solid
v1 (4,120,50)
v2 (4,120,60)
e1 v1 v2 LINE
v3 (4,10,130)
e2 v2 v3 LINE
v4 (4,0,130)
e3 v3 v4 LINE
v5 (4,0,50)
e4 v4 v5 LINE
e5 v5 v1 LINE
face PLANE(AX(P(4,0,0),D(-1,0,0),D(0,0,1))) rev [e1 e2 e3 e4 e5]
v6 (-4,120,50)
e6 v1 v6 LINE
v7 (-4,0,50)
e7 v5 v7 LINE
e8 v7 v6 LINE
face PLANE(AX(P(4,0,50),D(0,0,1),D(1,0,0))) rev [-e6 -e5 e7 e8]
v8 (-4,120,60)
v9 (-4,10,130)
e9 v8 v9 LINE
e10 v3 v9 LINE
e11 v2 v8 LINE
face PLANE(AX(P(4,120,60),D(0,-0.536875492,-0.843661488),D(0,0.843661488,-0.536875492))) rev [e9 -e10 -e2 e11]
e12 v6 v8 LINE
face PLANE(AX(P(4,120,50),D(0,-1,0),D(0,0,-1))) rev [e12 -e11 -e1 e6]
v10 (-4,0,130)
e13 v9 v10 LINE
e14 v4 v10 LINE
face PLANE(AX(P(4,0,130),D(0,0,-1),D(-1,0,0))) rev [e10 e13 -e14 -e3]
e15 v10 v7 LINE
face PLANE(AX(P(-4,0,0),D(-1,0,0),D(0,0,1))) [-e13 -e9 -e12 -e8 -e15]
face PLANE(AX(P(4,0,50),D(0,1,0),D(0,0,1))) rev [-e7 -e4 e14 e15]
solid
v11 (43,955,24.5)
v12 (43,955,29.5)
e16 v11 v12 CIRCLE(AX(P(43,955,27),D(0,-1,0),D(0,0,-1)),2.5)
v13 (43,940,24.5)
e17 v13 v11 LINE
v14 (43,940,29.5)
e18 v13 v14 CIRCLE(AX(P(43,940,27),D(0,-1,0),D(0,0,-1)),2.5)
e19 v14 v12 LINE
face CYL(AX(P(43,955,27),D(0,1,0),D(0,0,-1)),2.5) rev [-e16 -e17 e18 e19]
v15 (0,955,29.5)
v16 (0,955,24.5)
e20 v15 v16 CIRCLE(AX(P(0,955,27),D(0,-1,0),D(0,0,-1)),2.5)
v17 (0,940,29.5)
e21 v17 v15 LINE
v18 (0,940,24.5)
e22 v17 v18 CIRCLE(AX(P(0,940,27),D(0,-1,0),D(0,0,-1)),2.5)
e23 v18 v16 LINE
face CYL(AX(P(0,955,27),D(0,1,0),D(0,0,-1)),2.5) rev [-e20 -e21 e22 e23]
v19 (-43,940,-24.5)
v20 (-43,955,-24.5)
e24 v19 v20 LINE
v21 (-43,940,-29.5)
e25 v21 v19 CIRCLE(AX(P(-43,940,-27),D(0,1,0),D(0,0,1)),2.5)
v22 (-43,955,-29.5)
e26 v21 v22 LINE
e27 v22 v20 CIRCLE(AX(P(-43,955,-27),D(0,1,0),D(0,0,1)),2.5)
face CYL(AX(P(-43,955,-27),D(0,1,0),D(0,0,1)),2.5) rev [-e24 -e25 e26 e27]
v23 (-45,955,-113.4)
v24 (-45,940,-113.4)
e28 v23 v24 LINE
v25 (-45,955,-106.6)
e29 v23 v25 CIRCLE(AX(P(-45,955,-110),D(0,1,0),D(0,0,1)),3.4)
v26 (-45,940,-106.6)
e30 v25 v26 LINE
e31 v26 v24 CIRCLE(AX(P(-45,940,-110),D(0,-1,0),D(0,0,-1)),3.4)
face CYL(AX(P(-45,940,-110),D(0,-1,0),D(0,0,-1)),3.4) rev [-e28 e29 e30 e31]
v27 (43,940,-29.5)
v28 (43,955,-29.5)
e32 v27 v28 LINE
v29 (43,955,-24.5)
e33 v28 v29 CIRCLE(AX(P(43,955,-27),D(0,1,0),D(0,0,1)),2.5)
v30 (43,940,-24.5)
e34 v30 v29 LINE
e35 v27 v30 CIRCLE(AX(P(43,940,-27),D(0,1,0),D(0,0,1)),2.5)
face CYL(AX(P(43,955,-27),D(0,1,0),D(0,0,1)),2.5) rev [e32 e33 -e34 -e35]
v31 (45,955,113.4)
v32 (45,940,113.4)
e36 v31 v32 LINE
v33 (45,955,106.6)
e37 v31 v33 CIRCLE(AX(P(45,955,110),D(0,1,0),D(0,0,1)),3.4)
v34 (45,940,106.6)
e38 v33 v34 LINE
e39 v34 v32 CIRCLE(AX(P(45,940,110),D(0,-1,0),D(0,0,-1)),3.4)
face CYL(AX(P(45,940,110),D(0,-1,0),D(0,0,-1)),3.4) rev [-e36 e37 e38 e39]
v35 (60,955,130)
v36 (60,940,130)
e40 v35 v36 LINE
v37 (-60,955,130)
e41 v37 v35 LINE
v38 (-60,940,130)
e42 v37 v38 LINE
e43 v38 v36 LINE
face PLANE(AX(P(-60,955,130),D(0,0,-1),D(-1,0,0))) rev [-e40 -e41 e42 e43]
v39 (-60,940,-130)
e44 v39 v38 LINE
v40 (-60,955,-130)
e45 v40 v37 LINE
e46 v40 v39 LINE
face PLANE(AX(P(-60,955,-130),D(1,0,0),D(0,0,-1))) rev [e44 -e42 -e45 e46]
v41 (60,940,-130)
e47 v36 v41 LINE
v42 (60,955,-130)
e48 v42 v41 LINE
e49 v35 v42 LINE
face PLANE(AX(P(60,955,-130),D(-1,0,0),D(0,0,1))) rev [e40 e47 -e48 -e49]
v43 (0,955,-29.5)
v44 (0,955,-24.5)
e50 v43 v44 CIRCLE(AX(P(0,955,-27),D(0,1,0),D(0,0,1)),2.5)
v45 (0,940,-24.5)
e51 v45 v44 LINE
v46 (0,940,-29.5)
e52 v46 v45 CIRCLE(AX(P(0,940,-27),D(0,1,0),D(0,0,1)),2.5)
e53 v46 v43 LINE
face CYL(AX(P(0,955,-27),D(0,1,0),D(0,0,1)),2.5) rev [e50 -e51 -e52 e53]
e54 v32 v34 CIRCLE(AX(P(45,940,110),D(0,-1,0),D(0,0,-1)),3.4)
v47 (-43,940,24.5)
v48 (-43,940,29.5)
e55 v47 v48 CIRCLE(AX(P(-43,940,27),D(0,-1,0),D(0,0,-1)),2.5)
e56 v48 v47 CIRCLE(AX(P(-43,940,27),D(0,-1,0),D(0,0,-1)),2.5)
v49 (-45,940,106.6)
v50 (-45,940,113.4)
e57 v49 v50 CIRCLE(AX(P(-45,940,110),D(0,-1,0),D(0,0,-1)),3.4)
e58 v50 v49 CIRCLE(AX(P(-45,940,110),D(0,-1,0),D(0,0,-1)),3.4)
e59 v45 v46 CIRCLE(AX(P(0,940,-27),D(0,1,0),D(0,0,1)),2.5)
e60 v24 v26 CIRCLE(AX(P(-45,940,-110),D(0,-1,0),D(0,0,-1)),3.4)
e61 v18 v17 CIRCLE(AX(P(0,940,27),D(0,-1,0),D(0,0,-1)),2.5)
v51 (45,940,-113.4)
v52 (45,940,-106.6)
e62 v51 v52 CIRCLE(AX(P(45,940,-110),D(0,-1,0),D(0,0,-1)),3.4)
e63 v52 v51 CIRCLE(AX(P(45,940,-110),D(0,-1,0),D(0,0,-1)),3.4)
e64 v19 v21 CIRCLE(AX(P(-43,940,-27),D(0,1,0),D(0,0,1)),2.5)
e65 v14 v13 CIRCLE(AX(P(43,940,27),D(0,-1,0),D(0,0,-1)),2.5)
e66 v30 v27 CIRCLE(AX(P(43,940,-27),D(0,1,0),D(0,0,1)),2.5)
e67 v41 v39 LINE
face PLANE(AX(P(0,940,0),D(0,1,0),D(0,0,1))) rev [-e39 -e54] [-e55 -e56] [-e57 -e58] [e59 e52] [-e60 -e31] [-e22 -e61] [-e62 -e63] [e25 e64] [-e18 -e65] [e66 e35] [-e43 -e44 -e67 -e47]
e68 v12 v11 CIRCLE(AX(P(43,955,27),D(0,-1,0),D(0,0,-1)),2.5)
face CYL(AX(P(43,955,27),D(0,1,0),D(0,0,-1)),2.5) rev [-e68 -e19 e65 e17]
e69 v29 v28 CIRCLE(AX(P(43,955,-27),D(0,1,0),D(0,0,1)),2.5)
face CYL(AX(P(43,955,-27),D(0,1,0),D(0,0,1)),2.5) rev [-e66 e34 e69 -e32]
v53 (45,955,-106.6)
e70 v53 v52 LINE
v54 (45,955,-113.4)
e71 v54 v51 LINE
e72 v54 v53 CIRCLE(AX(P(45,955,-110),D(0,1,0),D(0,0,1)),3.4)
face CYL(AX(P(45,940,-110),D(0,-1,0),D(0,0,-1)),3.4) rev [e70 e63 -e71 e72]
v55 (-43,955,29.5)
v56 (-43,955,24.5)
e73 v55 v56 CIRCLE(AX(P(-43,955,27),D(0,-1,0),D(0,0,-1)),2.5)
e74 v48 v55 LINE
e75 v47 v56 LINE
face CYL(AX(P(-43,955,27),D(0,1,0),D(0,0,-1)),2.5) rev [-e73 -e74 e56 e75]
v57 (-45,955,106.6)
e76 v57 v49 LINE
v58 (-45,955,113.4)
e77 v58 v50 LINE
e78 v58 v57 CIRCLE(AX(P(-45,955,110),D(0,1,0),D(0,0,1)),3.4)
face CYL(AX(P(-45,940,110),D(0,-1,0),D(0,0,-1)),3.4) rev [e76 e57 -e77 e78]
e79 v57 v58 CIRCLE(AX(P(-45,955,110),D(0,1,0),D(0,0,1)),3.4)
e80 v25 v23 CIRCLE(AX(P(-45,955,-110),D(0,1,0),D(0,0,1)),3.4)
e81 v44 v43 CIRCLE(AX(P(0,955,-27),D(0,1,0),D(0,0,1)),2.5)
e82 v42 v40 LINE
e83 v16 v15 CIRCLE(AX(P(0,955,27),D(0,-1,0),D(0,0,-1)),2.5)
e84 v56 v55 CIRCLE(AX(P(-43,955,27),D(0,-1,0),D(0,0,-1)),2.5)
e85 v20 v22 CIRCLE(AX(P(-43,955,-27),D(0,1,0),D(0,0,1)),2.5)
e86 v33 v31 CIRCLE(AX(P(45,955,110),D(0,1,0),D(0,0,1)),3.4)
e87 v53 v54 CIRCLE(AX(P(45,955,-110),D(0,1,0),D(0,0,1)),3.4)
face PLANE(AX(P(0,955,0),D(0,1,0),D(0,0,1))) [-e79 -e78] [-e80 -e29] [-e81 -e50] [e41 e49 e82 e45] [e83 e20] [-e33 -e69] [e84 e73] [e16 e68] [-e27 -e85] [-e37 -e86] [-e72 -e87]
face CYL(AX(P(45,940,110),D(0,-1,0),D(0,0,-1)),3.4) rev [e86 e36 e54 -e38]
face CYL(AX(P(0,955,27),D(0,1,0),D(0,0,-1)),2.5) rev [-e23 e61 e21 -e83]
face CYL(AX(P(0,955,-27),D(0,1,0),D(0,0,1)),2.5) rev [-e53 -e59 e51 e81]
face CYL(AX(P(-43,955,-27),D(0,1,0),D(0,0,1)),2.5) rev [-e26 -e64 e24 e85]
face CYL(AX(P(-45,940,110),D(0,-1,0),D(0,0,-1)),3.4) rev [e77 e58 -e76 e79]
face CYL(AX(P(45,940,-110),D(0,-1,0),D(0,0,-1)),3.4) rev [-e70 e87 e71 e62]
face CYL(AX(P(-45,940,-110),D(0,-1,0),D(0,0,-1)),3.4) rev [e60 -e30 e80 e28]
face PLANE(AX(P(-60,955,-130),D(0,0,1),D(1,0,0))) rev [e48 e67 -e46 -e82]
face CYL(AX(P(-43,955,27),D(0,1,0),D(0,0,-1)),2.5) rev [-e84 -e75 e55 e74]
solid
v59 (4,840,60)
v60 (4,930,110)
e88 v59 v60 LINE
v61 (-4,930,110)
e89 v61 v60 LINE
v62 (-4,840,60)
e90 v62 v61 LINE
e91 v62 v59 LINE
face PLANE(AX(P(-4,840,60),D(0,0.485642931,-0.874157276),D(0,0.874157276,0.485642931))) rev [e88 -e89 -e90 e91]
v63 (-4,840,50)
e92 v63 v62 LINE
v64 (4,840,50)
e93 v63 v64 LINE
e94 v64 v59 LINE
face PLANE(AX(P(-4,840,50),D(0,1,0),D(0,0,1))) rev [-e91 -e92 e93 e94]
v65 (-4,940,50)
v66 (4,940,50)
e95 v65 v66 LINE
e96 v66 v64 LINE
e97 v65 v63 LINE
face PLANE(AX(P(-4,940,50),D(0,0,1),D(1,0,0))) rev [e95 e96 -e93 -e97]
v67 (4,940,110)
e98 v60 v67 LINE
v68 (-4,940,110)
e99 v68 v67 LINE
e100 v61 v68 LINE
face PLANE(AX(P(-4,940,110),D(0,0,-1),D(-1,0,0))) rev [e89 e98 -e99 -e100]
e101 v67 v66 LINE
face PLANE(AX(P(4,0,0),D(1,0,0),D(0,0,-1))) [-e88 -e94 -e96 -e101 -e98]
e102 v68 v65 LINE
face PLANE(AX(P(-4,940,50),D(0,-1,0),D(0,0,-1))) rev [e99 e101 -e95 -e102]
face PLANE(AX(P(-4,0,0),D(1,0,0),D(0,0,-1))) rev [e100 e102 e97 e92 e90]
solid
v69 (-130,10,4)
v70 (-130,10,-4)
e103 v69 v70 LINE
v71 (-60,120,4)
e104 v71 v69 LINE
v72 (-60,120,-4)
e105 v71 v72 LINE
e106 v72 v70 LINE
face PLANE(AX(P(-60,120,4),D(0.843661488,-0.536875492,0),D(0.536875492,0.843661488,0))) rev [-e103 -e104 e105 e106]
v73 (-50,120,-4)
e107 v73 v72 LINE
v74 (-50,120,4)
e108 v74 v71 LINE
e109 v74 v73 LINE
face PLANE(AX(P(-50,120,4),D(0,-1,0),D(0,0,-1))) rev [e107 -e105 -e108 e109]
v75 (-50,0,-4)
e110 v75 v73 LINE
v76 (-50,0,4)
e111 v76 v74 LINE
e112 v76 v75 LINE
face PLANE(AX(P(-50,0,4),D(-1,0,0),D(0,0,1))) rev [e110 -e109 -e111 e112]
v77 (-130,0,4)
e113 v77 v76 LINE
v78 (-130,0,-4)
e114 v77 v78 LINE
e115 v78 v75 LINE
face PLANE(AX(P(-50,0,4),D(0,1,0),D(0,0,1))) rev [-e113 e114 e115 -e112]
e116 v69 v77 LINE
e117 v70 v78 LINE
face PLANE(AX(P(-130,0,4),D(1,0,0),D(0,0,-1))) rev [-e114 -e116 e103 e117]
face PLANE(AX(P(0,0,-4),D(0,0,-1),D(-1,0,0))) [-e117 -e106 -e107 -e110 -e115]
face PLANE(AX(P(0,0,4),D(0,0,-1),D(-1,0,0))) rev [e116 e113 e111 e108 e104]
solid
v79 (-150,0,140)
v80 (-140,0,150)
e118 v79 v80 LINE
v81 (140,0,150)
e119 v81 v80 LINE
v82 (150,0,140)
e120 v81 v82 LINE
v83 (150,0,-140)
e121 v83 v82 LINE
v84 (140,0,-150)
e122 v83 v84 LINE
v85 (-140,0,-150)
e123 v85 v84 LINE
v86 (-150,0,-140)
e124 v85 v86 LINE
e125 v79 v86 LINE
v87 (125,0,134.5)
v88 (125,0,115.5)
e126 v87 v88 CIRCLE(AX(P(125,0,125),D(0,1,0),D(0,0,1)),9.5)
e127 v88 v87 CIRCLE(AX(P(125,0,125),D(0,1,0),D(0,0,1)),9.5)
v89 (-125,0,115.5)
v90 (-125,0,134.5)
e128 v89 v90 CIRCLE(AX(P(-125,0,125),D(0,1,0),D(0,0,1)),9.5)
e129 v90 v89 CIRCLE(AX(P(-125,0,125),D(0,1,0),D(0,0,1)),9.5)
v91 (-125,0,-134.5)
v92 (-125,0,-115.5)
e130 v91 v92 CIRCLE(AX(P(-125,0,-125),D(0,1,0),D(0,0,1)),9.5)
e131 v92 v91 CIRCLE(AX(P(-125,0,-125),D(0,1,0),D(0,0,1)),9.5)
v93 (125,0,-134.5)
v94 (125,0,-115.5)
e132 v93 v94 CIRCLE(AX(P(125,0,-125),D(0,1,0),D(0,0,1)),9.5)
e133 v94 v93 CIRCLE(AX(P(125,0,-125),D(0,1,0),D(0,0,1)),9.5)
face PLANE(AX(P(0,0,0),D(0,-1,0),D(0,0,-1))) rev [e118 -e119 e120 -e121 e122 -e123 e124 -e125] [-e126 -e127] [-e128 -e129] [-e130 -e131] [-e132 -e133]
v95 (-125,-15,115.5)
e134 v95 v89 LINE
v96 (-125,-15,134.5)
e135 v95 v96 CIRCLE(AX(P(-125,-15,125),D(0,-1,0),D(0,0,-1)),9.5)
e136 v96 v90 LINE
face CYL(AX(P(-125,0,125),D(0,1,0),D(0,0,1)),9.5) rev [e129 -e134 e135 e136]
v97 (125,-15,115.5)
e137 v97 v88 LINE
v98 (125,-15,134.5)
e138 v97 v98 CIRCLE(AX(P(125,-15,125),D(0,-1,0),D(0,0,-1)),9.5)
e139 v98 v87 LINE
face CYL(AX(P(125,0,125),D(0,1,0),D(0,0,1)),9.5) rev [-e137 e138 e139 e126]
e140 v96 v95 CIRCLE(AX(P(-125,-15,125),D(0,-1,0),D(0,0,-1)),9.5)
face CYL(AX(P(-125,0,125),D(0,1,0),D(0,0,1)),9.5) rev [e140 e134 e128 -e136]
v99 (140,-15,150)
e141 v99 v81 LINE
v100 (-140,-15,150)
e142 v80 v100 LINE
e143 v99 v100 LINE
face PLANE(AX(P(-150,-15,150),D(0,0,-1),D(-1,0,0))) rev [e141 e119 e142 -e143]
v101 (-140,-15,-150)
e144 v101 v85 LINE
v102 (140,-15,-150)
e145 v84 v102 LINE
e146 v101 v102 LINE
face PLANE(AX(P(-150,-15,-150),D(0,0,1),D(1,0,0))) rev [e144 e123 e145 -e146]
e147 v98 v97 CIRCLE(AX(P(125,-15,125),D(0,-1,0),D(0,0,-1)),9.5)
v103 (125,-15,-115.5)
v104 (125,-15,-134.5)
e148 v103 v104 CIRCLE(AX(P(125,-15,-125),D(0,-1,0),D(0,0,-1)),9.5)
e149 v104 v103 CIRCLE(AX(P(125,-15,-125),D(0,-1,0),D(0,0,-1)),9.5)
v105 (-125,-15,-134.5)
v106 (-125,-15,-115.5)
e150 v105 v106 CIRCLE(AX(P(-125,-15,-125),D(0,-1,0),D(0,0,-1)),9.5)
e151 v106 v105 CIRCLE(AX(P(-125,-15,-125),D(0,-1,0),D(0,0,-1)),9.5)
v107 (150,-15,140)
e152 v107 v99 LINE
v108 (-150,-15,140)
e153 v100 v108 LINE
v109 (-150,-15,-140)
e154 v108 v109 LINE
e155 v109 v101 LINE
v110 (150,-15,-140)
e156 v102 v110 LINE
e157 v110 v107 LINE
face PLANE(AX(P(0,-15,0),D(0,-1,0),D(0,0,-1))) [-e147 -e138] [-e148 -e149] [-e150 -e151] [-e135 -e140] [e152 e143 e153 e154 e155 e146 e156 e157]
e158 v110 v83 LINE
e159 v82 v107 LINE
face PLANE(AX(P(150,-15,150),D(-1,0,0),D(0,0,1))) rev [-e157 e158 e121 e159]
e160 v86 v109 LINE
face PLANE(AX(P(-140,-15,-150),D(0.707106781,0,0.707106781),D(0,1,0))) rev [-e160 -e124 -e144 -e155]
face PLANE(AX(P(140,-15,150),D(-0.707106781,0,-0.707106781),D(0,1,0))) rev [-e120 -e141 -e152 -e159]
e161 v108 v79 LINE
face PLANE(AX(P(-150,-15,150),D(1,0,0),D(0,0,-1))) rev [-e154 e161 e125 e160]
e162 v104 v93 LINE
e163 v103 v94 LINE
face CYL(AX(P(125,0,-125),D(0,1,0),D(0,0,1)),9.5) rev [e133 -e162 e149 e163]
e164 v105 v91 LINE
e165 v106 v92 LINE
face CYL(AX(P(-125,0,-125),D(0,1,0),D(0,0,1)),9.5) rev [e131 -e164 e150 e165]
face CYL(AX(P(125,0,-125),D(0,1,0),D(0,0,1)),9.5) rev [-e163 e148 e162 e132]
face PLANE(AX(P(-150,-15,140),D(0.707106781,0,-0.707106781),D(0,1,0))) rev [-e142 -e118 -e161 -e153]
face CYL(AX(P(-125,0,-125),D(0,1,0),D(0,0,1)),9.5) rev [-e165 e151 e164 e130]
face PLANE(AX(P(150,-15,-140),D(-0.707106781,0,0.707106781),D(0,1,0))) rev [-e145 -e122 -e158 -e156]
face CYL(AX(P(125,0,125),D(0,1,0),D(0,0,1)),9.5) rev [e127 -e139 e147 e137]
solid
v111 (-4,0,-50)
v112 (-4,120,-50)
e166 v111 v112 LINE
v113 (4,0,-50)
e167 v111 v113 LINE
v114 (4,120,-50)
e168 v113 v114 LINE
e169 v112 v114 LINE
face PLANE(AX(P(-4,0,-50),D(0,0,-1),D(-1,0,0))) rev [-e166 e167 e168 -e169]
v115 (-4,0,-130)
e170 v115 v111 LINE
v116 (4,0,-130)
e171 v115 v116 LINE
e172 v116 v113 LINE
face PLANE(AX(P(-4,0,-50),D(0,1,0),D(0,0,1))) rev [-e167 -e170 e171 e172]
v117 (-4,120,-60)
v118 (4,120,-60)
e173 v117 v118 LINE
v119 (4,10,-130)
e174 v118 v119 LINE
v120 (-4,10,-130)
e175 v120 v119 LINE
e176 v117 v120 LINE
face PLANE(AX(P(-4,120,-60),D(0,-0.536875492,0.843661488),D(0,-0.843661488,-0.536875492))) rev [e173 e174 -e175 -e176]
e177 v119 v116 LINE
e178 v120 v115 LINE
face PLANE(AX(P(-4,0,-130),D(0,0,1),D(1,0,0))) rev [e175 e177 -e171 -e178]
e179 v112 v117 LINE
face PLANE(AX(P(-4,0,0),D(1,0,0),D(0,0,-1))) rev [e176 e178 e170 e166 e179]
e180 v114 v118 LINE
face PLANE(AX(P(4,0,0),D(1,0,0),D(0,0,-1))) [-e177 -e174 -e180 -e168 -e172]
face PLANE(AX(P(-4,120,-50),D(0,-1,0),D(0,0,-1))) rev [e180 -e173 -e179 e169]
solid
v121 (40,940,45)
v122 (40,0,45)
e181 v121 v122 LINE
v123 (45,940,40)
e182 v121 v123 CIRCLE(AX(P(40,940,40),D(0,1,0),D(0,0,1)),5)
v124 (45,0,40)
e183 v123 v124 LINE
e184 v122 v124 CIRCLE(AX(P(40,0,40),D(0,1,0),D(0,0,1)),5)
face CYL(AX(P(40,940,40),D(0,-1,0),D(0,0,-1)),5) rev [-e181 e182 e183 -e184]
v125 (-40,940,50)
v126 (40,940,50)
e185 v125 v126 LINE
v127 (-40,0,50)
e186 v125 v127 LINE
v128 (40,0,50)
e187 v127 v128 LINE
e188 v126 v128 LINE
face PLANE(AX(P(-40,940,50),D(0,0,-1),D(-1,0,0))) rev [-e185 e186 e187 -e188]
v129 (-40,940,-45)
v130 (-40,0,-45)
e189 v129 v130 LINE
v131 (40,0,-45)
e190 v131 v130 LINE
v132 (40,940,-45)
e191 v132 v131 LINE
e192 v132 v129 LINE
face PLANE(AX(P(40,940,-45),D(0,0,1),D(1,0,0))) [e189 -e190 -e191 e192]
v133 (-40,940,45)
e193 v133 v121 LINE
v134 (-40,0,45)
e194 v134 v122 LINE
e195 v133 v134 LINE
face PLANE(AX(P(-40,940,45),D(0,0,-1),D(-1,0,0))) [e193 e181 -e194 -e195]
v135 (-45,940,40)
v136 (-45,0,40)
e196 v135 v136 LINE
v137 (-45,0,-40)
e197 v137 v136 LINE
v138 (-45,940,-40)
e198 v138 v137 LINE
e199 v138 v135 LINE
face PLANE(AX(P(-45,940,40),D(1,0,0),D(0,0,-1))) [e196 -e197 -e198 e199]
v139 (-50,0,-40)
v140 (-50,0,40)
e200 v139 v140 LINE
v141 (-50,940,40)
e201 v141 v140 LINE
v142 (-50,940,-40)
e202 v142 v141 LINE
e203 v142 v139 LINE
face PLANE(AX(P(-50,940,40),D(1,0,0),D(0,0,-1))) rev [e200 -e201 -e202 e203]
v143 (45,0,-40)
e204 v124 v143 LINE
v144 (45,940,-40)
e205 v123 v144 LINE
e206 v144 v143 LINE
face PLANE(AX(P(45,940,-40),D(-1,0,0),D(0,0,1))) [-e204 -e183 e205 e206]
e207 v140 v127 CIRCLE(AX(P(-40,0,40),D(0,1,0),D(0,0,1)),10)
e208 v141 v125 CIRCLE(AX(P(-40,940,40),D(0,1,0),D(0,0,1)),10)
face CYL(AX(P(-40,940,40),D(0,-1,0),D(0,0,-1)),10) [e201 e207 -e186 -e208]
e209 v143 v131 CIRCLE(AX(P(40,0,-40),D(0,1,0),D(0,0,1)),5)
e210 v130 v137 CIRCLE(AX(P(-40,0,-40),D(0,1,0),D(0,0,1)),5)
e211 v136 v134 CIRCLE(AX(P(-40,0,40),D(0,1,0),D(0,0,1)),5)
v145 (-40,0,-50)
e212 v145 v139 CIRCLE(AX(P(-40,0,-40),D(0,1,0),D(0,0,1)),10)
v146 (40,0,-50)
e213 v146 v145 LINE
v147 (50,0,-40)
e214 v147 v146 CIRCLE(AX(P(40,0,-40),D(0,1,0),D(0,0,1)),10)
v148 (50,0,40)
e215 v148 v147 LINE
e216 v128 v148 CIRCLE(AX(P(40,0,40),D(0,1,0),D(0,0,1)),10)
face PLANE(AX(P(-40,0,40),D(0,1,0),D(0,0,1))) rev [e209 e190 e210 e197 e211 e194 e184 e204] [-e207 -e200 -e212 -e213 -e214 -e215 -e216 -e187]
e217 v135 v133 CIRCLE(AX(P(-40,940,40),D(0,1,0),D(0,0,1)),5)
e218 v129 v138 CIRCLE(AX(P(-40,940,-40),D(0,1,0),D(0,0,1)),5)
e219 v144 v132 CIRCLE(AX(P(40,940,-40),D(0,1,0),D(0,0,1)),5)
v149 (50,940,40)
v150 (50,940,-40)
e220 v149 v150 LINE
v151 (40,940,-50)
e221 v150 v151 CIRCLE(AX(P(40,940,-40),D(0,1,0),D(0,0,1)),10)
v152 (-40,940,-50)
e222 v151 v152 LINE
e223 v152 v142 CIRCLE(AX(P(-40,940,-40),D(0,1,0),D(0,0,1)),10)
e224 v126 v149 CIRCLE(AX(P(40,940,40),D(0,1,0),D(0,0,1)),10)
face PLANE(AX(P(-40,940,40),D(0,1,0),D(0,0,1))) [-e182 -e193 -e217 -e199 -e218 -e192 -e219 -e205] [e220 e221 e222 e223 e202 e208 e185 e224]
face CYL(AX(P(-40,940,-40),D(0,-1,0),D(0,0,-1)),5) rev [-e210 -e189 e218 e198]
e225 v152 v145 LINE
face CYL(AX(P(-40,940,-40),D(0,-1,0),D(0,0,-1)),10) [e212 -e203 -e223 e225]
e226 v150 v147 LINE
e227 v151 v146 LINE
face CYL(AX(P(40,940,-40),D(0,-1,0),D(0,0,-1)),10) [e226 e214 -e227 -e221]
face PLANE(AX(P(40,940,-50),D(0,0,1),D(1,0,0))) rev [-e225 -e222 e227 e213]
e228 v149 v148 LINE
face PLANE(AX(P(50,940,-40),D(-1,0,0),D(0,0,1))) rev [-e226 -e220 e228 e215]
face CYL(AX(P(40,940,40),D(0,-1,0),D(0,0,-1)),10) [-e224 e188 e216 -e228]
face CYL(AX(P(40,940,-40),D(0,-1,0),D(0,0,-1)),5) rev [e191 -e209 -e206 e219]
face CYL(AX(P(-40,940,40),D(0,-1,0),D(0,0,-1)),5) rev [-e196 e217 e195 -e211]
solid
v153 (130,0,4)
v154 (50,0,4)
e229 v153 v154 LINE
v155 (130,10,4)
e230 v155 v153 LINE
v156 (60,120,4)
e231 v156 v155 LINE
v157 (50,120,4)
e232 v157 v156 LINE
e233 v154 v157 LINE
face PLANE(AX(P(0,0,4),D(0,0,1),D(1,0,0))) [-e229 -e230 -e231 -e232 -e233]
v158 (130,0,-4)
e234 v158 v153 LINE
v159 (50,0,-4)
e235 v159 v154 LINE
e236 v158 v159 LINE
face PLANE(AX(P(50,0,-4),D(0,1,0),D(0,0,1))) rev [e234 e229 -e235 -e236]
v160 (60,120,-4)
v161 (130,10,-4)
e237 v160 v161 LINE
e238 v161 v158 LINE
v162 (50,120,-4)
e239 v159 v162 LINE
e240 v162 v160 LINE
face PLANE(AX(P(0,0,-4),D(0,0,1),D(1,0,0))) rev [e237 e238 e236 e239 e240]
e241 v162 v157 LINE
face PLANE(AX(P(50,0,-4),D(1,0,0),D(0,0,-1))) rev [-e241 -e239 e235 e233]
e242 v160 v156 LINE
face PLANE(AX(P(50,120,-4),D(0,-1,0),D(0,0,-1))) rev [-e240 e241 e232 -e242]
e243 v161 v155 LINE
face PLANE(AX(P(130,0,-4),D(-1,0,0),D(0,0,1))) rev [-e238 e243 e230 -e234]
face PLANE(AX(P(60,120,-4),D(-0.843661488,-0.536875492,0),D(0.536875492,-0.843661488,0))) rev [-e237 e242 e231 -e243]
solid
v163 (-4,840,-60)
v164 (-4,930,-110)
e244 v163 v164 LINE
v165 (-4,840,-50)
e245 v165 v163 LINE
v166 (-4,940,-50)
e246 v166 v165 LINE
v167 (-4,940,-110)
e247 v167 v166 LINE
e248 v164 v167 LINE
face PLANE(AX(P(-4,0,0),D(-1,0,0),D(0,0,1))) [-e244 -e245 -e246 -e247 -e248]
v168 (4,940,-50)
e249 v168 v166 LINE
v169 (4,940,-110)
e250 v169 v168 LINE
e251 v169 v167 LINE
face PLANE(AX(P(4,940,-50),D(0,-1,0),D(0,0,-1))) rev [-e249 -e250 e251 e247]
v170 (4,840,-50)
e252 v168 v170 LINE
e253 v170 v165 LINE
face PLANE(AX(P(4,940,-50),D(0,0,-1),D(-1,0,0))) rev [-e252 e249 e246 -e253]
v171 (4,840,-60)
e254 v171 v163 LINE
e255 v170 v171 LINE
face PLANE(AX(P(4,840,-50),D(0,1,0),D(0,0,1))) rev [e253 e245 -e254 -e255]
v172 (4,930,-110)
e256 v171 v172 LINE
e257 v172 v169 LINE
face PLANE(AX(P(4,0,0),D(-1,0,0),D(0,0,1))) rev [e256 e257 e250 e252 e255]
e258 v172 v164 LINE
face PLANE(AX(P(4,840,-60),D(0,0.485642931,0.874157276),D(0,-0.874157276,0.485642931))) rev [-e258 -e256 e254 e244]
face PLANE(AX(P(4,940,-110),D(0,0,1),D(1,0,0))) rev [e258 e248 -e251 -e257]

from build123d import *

# Parameters (mm, degrees)
F_100_X_100_X_5_1_DEPTH          = 940
SKETCH_4_W                       = 300
SKETCH_4_H                       = 300
EXTRUDE_1_DEPTH                  = 15
SKETCH_5_W                       = 120
SKETCH_5_H                       = 260
EXTRUDE_2_DEPTH                  = 15
GUSSET_1_THICKNESS               = 8
GUSSET_2_THICKNESS               = 8
GUSSET_3_THICKNESS               = 8
GUSSET_4_THICKNESS               = 8
GUSSET_5_THICKNESS               = 8
GUSSET_6_THICKNESS               = 8
HOLE_WIZARD_19_0_19_1_AT_2_COUNT = 2
HOLE_WIZARD_19_0_19_1_AT_2_PITCH = 250
HOLE_WIZARD_19_0_19_1_AT_3_COUNT = 2
HOLE_WIZARD_19_0_19_1_AT_3_PITCH = 353.553390593
HOLE_WIZARD_19_0_19_1_AT_4_COUNT = 2
HOLE_WIZARD_19_0_19_1_AT_4_PITCH = 250
HOLE_WIZARD_M8_1_AT_2_COUNT      = 2
HOLE_WIZARD_M8_1_AT_2_PITCH      = 90
HOLE_WIZARD_M8_1_AT_3_COUNT      = 2
HOLE_WIZARD_M8_1_AT_3_PITCH      = 237.69728648
HOLE_WIZARD_M8_1_AT_4_COUNT      = 2
HOLE_WIZARD_M8_1_AT_4_PITCH      = 220
CHAMFER_1_SIZE                   = 10
HOLE_WIZARD_M6_1_AT_2_COUNT      = 2
HOLE_WIZARD_M6_1_AT_2_PITCH      = 43


with BuildPart() as part:
    # Sketch12 → 方形管 100 X 100 X 5(1) (new body)
    with BuildSketch(Plane(origin=(0, 0, 0), x_dir=(-1, 0, 0), z_dir=(0, 1, 0))):
        with BuildLine():
            Line((-40, -50), (40, -50))
            ThreePointArc((40, -50), (47.071067812, -47.071067812), (50, -40))
            Line((50, -40), (50, 40))
            ThreePointArc((50, 40), (47.071067812, 47.071067812), (40, 50))
            Line((40, 50), (-40, 50))
            ThreePointArc((-40, 50), (-47.071067812, 47.071067812), (-50, 40))
            Line((-50, 40), (-50, -40))
            ThreePointArc((-50, -40), (-47.071067812, -47.071067812), (-40, -50))
        make_face()
        with BuildLine():
            Line((-40, -45), (40, -45))
            ThreePointArc((40, -45), (43.535533906, -43.535533906), (45, -40))
            Line((45, -40), (45, 40))
            ThreePointArc((45, 40), (43.535533906, 43.535533906), (40, 45))
            Line((40, 45), (-40, 45))
            ThreePointArc((-40, 45), (-43.535533906, 43.535533906), (-45, 40))
            Line((-45, 40), (-45, -40))
            ThreePointArc((-45, -40), (-43.535533906, -43.535533906), (-40, -45))
        make_face(mode=Mode.SUBTRACT)
    extrude(amount=F_100_X_100_X_5_1_DEPTH)


with BuildPart() as body_2:
    # 草图4 → 凸台-拉伸1 (new body)
    with BuildSketch(Plane.XZ):
        Rectangle(SKETCH_4_W, SKETCH_4_H)
    extrude(amount=EXTRUDE_1_DEPTH)

    # 草图13 → Ø19.0 (19) 直径孔1 (revolve, cut)
    with BuildSketch(Plane(origin=(125, 0, 125), x_dir=(0, 0, 1), z_dir=(1, 0, 0))):
        Polygon((0, 0), (0, 33.208175881), (9.5, 27.5), (9.5, 0), align=None)
    hole_wizard_19_0_19_1 = revolve(axis=Axis((125, 6.35, 125), (0, -1, 0)), mode=Mode.SUBTRACT)

    # Ø19.0 (19) 直径孔1 at 2: Ø19.0 (19) 直径孔1 ×2
    with Locations(*[(0, 0, -i * HOLE_WIZARD_19_0_19_1_AT_2_PITCH) for i in range(1, HOLE_WIZARD_19_0_19_1_AT_2_COUNT)]):
        add(hole_wizard_19_0_19_1, mode=Mode.SUBTRACT)

    # Ø19.0 (19) 直径孔1 at 3: Ø19.0 (19) 直径孔1 ×2
    with Locations(*[Vector(-0.7071067811865476, 0, -0.7071067811865476) * (i * HOLE_WIZARD_19_0_19_1_AT_3_PITCH) for i in range(1, HOLE_WIZARD_19_0_19_1_AT_3_COUNT)]):
        add(hole_wizard_19_0_19_1, mode=Mode.SUBTRACT)

    # Ø19.0 (19) 直径孔1 at 4: Ø19.0 (19) 直径孔1 ×2
    with Locations(*[(-i * HOLE_WIZARD_19_0_19_1_AT_4_PITCH, 0, 0) for i in range(1, HOLE_WIZARD_19_0_19_1_AT_4_COUNT)]):
        add(hole_wizard_19_0_19_1, mode=Mode.SUBTRACT)

    # 倒角1
    chamfer_1_edges = [body_2.edges().sort_by_distance(p)[0] for p in [
        (150, -7.5, -150),
        (-150, -7.5, -150),
        (-150, -7.5, 150),
        (150, -7.5, 150),
    ]]
    chamfer(chamfer_1_edges, length=CHAMFER_1_SIZE)


with BuildPart() as body_3:
    # 草图5 → 凸台-拉伸2 (new body)
    with BuildSketch(Plane(origin=(0, 940, 0), x_dir=(1, 0, 0), z_dir=(0, 1, 0))):
        Rectangle(SKETCH_5_W, SKETCH_5_H)
    extrude(amount=EXTRUDE_2_DEPTH)

    # 草图15 → M8 螺纹孔1 (revolve, cut)
    with BuildSketch(Plane(origin=(45, 940, 110), x_dir=(0, 0, -1), z_dir=(1, 0, 0))):
        Polygon((0, 0), (0, 21.792926105), (3.4, 19.75), (3.4, 0), align=None)
    hole_wizard_m8_1 = revolve(axis=Axis((45, 933.65, 110), (0, 1, 0)), mode=Mode.SUBTRACT)

    # M8 螺纹孔1 at 2: M8 螺纹孔1 ×2
    with Locations(*[(-i * HOLE_WIZARD_M8_1_AT_2_PITCH, 0, 0) for i in range(1, HOLE_WIZARD_M8_1_AT_2_COUNT)]):
        add(hole_wizard_m8_1, mode=Mode.SUBTRACT)

    # M8 螺纹孔1 at 3: M8 螺纹孔1 ×2
    with Locations(*[Vector(-0.37863284572050415, 0, -0.9255469562056767) * (i * HOLE_WIZARD_M8_1_AT_3_PITCH) for i in range(1, HOLE_WIZARD_M8_1_AT_3_COUNT)]):
        add(hole_wizard_m8_1, mode=Mode.SUBTRACT)

    # M8 螺纹孔1 at 4: M8 螺纹孔1 ×2
    with Locations(*[(0, 0, -i * HOLE_WIZARD_M8_1_AT_4_PITCH) for i in range(1, HOLE_WIZARD_M8_1_AT_4_COUNT)]):
        add(hole_wizard_m8_1, mode=Mode.SUBTRACT)

    # 草图19 → M6 螺纹孔1 (revolve, cut)
    with BuildSketch(Plane(origin=(-43, 955, -27), x_dir=(0, 0, 1), z_dir=(1, 0, 0))):
        Polygon((0, 0), (0, 16.502151548), (2.5, 15), (2.5, 0), align=None)
    hole_wizard_m6_1 = revolve(axis=Axis((-43, 961.35, -27), (0, -1, 0)), mode=Mode.SUBTRACT)

    # M6 螺纹孔1 at 2: M6 螺纹孔1 ×2
    with Locations(*[(i * HOLE_WIZARD_M6_1_AT_2_PITCH, 0, 0) for i in range(1, HOLE_WIZARD_M6_1_AT_2_COUNT)]):
        add(hole_wizard_m6_1, mode=Mode.SUBTRACT)

    # 草图20 → M6 螺纹孔2 (revolve, cut)
    with BuildSketch(Plane(origin=(43, 955, -27), x_dir=(0, 0, 1), z_dir=(1, 0, 0))):
        Polygon((0, 0), (0, 16.502151548), (2.5, 15), (2.5, 0), align=None)
    hole_wizard_m6_2 = revolve(axis=Axis((43, 961.35, -27), (0, -1, 0)), mode=Mode.SUBTRACT)

    # 镜向1: M6 螺纹孔1, M6 螺纹孔2 across plane
    add(hole_wizard_m6_1.mirror(Plane.XY), mode=Mode.SUBTRACT)
    add(hole_wizard_m6_2.mirror(Plane.XY), mode=Mode.SUBTRACT)

    # 镜向1 copy 1 sketch → 镜向1 copy 1 (revolve, cut)
    with BuildSketch(Plane(origin=(0, 955, 27), x_dir=(0, 0, -1), z_dir=(1, 0, 0))):
        Polygon((0, 0), (0, -16.502151548), (2.5, -15), (2.5, 0), align=None)
    revolve(axis=Axis((0, 961.35, 27), (0, 1, 0)), mode=Mode.SUBTRACT)


with BuildPart() as body_4:
    # Gusset 1: a gusset: a plate 8.0 thick in the corner of two members, its outline drawn in place
    gusset_1_outline = Wire([Line((50, 0, -4), (50, 120, -4)), Line((50, 120, -4), (60, 120, -4)), Line((60, 120, -4), (130, 10, -4)), Line((130, 10, -4), (130, 0, -4)), Line((130, 0, -4), (50, 0, -4))])
    add(extrude(Face(gusset_1_outline), amount=GUSSET_1_THICKNESS, dir=(0, 0, 1)))


with BuildPart() as body_5:
    # Gusset 2: a gusset: a plate 8.0 thick in the corner of two members, its outline drawn in place
    gusset_2_outline = Wire([Line((-4, 0, -50), (-4, 120, -50)), Line((-4, 120, -50), (-4, 120, -60)), Line((-4, 120, -60), (-4, 10, -130)), Line((-4, 10, -130), (-4, 0, -130)), Line((-4, 0, -130), (-4, 0, -50))])
    add(extrude(Face(gusset_2_outline), amount=GUSSET_2_THICKNESS, dir=(1, 0, 0)))


with BuildPart() as body_6:
    # Gusset 3: a gusset: a plate 8.0 thick in the corner of two members, its outline drawn in place
    gusset_3_outline = Wire([Line((-50, 0, 4), (-50, 120, 4)), Line((-50, 120, 4), (-60, 120, 4)), Line((-60, 120, 4), (-130, 10, 4)), Line((-130, 10, 4), (-130, 0, 4)), Line((-130, 0, 4), (-50, 0, 4))])
    add(extrude(Face(gusset_3_outline), amount=GUSSET_3_THICKNESS, dir=(0, 0, -1)))


with BuildPart() as body_7:
    # Gusset 4: a gusset: a plate 8.0 thick in the corner of two members, its outline drawn in place
    gusset_4_outline = Wire([Line((4, 0, 50), (4, 120, 50)), Line((4, 120, 50), (4, 120, 60)), Line((4, 120, 60), (4, 10, 130)), Line((4, 10, 130), (4, 0, 130)), Line((4, 0, 130), (4, 0, 50))])
    add(extrude(Face(gusset_4_outline), amount=GUSSET_4_THICKNESS, dir=(-1, 0, 0)))


with BuildPart() as body_8:
    # Gusset 5: a gusset: a plate 8.0 thick in the corner of two members, its outline drawn in place
    gusset_5_outline = Wire([Line((4, 940, -50), (4, 840, -50)), Line((4, 840, -50), (4, 840, -60)), Line((4, 840, -60), (4, 930, -110)), Line((4, 930, -110), (4, 940, -110)), Line((4, 940, -110), (4, 940, -50))])
    add(extrude(Face(gusset_5_outline), amount=GUSSET_5_THICKNESS, dir=(-1, 0, 0)))


with BuildPart() as body_9:
    # Gusset 6: a gusset: a plate 8.0 thick in the corner of two members, its outline drawn in place
    gusset_6_outline = Wire([Line((-4, 940, 50), (-4, 840, 50)), Line((-4, 840, 50), (-4, 840, 60)), Line((-4, 840, 60), (-4, 930, 110)), Line((-4, 930, 110), (-4, 940, 110)), Line((-4, 940, 110), (-4, 940, 50))])
    add(extrude(Face(gusset_6_outline), amount=GUSSET_6_THICKNESS, dir=(1, 0, 0)))


solid = Compound([part.part, body_2.part, body_3.part, body_4.part, body_5.part, body_6.part, body_7.part, body_8.part, body_9.part])
